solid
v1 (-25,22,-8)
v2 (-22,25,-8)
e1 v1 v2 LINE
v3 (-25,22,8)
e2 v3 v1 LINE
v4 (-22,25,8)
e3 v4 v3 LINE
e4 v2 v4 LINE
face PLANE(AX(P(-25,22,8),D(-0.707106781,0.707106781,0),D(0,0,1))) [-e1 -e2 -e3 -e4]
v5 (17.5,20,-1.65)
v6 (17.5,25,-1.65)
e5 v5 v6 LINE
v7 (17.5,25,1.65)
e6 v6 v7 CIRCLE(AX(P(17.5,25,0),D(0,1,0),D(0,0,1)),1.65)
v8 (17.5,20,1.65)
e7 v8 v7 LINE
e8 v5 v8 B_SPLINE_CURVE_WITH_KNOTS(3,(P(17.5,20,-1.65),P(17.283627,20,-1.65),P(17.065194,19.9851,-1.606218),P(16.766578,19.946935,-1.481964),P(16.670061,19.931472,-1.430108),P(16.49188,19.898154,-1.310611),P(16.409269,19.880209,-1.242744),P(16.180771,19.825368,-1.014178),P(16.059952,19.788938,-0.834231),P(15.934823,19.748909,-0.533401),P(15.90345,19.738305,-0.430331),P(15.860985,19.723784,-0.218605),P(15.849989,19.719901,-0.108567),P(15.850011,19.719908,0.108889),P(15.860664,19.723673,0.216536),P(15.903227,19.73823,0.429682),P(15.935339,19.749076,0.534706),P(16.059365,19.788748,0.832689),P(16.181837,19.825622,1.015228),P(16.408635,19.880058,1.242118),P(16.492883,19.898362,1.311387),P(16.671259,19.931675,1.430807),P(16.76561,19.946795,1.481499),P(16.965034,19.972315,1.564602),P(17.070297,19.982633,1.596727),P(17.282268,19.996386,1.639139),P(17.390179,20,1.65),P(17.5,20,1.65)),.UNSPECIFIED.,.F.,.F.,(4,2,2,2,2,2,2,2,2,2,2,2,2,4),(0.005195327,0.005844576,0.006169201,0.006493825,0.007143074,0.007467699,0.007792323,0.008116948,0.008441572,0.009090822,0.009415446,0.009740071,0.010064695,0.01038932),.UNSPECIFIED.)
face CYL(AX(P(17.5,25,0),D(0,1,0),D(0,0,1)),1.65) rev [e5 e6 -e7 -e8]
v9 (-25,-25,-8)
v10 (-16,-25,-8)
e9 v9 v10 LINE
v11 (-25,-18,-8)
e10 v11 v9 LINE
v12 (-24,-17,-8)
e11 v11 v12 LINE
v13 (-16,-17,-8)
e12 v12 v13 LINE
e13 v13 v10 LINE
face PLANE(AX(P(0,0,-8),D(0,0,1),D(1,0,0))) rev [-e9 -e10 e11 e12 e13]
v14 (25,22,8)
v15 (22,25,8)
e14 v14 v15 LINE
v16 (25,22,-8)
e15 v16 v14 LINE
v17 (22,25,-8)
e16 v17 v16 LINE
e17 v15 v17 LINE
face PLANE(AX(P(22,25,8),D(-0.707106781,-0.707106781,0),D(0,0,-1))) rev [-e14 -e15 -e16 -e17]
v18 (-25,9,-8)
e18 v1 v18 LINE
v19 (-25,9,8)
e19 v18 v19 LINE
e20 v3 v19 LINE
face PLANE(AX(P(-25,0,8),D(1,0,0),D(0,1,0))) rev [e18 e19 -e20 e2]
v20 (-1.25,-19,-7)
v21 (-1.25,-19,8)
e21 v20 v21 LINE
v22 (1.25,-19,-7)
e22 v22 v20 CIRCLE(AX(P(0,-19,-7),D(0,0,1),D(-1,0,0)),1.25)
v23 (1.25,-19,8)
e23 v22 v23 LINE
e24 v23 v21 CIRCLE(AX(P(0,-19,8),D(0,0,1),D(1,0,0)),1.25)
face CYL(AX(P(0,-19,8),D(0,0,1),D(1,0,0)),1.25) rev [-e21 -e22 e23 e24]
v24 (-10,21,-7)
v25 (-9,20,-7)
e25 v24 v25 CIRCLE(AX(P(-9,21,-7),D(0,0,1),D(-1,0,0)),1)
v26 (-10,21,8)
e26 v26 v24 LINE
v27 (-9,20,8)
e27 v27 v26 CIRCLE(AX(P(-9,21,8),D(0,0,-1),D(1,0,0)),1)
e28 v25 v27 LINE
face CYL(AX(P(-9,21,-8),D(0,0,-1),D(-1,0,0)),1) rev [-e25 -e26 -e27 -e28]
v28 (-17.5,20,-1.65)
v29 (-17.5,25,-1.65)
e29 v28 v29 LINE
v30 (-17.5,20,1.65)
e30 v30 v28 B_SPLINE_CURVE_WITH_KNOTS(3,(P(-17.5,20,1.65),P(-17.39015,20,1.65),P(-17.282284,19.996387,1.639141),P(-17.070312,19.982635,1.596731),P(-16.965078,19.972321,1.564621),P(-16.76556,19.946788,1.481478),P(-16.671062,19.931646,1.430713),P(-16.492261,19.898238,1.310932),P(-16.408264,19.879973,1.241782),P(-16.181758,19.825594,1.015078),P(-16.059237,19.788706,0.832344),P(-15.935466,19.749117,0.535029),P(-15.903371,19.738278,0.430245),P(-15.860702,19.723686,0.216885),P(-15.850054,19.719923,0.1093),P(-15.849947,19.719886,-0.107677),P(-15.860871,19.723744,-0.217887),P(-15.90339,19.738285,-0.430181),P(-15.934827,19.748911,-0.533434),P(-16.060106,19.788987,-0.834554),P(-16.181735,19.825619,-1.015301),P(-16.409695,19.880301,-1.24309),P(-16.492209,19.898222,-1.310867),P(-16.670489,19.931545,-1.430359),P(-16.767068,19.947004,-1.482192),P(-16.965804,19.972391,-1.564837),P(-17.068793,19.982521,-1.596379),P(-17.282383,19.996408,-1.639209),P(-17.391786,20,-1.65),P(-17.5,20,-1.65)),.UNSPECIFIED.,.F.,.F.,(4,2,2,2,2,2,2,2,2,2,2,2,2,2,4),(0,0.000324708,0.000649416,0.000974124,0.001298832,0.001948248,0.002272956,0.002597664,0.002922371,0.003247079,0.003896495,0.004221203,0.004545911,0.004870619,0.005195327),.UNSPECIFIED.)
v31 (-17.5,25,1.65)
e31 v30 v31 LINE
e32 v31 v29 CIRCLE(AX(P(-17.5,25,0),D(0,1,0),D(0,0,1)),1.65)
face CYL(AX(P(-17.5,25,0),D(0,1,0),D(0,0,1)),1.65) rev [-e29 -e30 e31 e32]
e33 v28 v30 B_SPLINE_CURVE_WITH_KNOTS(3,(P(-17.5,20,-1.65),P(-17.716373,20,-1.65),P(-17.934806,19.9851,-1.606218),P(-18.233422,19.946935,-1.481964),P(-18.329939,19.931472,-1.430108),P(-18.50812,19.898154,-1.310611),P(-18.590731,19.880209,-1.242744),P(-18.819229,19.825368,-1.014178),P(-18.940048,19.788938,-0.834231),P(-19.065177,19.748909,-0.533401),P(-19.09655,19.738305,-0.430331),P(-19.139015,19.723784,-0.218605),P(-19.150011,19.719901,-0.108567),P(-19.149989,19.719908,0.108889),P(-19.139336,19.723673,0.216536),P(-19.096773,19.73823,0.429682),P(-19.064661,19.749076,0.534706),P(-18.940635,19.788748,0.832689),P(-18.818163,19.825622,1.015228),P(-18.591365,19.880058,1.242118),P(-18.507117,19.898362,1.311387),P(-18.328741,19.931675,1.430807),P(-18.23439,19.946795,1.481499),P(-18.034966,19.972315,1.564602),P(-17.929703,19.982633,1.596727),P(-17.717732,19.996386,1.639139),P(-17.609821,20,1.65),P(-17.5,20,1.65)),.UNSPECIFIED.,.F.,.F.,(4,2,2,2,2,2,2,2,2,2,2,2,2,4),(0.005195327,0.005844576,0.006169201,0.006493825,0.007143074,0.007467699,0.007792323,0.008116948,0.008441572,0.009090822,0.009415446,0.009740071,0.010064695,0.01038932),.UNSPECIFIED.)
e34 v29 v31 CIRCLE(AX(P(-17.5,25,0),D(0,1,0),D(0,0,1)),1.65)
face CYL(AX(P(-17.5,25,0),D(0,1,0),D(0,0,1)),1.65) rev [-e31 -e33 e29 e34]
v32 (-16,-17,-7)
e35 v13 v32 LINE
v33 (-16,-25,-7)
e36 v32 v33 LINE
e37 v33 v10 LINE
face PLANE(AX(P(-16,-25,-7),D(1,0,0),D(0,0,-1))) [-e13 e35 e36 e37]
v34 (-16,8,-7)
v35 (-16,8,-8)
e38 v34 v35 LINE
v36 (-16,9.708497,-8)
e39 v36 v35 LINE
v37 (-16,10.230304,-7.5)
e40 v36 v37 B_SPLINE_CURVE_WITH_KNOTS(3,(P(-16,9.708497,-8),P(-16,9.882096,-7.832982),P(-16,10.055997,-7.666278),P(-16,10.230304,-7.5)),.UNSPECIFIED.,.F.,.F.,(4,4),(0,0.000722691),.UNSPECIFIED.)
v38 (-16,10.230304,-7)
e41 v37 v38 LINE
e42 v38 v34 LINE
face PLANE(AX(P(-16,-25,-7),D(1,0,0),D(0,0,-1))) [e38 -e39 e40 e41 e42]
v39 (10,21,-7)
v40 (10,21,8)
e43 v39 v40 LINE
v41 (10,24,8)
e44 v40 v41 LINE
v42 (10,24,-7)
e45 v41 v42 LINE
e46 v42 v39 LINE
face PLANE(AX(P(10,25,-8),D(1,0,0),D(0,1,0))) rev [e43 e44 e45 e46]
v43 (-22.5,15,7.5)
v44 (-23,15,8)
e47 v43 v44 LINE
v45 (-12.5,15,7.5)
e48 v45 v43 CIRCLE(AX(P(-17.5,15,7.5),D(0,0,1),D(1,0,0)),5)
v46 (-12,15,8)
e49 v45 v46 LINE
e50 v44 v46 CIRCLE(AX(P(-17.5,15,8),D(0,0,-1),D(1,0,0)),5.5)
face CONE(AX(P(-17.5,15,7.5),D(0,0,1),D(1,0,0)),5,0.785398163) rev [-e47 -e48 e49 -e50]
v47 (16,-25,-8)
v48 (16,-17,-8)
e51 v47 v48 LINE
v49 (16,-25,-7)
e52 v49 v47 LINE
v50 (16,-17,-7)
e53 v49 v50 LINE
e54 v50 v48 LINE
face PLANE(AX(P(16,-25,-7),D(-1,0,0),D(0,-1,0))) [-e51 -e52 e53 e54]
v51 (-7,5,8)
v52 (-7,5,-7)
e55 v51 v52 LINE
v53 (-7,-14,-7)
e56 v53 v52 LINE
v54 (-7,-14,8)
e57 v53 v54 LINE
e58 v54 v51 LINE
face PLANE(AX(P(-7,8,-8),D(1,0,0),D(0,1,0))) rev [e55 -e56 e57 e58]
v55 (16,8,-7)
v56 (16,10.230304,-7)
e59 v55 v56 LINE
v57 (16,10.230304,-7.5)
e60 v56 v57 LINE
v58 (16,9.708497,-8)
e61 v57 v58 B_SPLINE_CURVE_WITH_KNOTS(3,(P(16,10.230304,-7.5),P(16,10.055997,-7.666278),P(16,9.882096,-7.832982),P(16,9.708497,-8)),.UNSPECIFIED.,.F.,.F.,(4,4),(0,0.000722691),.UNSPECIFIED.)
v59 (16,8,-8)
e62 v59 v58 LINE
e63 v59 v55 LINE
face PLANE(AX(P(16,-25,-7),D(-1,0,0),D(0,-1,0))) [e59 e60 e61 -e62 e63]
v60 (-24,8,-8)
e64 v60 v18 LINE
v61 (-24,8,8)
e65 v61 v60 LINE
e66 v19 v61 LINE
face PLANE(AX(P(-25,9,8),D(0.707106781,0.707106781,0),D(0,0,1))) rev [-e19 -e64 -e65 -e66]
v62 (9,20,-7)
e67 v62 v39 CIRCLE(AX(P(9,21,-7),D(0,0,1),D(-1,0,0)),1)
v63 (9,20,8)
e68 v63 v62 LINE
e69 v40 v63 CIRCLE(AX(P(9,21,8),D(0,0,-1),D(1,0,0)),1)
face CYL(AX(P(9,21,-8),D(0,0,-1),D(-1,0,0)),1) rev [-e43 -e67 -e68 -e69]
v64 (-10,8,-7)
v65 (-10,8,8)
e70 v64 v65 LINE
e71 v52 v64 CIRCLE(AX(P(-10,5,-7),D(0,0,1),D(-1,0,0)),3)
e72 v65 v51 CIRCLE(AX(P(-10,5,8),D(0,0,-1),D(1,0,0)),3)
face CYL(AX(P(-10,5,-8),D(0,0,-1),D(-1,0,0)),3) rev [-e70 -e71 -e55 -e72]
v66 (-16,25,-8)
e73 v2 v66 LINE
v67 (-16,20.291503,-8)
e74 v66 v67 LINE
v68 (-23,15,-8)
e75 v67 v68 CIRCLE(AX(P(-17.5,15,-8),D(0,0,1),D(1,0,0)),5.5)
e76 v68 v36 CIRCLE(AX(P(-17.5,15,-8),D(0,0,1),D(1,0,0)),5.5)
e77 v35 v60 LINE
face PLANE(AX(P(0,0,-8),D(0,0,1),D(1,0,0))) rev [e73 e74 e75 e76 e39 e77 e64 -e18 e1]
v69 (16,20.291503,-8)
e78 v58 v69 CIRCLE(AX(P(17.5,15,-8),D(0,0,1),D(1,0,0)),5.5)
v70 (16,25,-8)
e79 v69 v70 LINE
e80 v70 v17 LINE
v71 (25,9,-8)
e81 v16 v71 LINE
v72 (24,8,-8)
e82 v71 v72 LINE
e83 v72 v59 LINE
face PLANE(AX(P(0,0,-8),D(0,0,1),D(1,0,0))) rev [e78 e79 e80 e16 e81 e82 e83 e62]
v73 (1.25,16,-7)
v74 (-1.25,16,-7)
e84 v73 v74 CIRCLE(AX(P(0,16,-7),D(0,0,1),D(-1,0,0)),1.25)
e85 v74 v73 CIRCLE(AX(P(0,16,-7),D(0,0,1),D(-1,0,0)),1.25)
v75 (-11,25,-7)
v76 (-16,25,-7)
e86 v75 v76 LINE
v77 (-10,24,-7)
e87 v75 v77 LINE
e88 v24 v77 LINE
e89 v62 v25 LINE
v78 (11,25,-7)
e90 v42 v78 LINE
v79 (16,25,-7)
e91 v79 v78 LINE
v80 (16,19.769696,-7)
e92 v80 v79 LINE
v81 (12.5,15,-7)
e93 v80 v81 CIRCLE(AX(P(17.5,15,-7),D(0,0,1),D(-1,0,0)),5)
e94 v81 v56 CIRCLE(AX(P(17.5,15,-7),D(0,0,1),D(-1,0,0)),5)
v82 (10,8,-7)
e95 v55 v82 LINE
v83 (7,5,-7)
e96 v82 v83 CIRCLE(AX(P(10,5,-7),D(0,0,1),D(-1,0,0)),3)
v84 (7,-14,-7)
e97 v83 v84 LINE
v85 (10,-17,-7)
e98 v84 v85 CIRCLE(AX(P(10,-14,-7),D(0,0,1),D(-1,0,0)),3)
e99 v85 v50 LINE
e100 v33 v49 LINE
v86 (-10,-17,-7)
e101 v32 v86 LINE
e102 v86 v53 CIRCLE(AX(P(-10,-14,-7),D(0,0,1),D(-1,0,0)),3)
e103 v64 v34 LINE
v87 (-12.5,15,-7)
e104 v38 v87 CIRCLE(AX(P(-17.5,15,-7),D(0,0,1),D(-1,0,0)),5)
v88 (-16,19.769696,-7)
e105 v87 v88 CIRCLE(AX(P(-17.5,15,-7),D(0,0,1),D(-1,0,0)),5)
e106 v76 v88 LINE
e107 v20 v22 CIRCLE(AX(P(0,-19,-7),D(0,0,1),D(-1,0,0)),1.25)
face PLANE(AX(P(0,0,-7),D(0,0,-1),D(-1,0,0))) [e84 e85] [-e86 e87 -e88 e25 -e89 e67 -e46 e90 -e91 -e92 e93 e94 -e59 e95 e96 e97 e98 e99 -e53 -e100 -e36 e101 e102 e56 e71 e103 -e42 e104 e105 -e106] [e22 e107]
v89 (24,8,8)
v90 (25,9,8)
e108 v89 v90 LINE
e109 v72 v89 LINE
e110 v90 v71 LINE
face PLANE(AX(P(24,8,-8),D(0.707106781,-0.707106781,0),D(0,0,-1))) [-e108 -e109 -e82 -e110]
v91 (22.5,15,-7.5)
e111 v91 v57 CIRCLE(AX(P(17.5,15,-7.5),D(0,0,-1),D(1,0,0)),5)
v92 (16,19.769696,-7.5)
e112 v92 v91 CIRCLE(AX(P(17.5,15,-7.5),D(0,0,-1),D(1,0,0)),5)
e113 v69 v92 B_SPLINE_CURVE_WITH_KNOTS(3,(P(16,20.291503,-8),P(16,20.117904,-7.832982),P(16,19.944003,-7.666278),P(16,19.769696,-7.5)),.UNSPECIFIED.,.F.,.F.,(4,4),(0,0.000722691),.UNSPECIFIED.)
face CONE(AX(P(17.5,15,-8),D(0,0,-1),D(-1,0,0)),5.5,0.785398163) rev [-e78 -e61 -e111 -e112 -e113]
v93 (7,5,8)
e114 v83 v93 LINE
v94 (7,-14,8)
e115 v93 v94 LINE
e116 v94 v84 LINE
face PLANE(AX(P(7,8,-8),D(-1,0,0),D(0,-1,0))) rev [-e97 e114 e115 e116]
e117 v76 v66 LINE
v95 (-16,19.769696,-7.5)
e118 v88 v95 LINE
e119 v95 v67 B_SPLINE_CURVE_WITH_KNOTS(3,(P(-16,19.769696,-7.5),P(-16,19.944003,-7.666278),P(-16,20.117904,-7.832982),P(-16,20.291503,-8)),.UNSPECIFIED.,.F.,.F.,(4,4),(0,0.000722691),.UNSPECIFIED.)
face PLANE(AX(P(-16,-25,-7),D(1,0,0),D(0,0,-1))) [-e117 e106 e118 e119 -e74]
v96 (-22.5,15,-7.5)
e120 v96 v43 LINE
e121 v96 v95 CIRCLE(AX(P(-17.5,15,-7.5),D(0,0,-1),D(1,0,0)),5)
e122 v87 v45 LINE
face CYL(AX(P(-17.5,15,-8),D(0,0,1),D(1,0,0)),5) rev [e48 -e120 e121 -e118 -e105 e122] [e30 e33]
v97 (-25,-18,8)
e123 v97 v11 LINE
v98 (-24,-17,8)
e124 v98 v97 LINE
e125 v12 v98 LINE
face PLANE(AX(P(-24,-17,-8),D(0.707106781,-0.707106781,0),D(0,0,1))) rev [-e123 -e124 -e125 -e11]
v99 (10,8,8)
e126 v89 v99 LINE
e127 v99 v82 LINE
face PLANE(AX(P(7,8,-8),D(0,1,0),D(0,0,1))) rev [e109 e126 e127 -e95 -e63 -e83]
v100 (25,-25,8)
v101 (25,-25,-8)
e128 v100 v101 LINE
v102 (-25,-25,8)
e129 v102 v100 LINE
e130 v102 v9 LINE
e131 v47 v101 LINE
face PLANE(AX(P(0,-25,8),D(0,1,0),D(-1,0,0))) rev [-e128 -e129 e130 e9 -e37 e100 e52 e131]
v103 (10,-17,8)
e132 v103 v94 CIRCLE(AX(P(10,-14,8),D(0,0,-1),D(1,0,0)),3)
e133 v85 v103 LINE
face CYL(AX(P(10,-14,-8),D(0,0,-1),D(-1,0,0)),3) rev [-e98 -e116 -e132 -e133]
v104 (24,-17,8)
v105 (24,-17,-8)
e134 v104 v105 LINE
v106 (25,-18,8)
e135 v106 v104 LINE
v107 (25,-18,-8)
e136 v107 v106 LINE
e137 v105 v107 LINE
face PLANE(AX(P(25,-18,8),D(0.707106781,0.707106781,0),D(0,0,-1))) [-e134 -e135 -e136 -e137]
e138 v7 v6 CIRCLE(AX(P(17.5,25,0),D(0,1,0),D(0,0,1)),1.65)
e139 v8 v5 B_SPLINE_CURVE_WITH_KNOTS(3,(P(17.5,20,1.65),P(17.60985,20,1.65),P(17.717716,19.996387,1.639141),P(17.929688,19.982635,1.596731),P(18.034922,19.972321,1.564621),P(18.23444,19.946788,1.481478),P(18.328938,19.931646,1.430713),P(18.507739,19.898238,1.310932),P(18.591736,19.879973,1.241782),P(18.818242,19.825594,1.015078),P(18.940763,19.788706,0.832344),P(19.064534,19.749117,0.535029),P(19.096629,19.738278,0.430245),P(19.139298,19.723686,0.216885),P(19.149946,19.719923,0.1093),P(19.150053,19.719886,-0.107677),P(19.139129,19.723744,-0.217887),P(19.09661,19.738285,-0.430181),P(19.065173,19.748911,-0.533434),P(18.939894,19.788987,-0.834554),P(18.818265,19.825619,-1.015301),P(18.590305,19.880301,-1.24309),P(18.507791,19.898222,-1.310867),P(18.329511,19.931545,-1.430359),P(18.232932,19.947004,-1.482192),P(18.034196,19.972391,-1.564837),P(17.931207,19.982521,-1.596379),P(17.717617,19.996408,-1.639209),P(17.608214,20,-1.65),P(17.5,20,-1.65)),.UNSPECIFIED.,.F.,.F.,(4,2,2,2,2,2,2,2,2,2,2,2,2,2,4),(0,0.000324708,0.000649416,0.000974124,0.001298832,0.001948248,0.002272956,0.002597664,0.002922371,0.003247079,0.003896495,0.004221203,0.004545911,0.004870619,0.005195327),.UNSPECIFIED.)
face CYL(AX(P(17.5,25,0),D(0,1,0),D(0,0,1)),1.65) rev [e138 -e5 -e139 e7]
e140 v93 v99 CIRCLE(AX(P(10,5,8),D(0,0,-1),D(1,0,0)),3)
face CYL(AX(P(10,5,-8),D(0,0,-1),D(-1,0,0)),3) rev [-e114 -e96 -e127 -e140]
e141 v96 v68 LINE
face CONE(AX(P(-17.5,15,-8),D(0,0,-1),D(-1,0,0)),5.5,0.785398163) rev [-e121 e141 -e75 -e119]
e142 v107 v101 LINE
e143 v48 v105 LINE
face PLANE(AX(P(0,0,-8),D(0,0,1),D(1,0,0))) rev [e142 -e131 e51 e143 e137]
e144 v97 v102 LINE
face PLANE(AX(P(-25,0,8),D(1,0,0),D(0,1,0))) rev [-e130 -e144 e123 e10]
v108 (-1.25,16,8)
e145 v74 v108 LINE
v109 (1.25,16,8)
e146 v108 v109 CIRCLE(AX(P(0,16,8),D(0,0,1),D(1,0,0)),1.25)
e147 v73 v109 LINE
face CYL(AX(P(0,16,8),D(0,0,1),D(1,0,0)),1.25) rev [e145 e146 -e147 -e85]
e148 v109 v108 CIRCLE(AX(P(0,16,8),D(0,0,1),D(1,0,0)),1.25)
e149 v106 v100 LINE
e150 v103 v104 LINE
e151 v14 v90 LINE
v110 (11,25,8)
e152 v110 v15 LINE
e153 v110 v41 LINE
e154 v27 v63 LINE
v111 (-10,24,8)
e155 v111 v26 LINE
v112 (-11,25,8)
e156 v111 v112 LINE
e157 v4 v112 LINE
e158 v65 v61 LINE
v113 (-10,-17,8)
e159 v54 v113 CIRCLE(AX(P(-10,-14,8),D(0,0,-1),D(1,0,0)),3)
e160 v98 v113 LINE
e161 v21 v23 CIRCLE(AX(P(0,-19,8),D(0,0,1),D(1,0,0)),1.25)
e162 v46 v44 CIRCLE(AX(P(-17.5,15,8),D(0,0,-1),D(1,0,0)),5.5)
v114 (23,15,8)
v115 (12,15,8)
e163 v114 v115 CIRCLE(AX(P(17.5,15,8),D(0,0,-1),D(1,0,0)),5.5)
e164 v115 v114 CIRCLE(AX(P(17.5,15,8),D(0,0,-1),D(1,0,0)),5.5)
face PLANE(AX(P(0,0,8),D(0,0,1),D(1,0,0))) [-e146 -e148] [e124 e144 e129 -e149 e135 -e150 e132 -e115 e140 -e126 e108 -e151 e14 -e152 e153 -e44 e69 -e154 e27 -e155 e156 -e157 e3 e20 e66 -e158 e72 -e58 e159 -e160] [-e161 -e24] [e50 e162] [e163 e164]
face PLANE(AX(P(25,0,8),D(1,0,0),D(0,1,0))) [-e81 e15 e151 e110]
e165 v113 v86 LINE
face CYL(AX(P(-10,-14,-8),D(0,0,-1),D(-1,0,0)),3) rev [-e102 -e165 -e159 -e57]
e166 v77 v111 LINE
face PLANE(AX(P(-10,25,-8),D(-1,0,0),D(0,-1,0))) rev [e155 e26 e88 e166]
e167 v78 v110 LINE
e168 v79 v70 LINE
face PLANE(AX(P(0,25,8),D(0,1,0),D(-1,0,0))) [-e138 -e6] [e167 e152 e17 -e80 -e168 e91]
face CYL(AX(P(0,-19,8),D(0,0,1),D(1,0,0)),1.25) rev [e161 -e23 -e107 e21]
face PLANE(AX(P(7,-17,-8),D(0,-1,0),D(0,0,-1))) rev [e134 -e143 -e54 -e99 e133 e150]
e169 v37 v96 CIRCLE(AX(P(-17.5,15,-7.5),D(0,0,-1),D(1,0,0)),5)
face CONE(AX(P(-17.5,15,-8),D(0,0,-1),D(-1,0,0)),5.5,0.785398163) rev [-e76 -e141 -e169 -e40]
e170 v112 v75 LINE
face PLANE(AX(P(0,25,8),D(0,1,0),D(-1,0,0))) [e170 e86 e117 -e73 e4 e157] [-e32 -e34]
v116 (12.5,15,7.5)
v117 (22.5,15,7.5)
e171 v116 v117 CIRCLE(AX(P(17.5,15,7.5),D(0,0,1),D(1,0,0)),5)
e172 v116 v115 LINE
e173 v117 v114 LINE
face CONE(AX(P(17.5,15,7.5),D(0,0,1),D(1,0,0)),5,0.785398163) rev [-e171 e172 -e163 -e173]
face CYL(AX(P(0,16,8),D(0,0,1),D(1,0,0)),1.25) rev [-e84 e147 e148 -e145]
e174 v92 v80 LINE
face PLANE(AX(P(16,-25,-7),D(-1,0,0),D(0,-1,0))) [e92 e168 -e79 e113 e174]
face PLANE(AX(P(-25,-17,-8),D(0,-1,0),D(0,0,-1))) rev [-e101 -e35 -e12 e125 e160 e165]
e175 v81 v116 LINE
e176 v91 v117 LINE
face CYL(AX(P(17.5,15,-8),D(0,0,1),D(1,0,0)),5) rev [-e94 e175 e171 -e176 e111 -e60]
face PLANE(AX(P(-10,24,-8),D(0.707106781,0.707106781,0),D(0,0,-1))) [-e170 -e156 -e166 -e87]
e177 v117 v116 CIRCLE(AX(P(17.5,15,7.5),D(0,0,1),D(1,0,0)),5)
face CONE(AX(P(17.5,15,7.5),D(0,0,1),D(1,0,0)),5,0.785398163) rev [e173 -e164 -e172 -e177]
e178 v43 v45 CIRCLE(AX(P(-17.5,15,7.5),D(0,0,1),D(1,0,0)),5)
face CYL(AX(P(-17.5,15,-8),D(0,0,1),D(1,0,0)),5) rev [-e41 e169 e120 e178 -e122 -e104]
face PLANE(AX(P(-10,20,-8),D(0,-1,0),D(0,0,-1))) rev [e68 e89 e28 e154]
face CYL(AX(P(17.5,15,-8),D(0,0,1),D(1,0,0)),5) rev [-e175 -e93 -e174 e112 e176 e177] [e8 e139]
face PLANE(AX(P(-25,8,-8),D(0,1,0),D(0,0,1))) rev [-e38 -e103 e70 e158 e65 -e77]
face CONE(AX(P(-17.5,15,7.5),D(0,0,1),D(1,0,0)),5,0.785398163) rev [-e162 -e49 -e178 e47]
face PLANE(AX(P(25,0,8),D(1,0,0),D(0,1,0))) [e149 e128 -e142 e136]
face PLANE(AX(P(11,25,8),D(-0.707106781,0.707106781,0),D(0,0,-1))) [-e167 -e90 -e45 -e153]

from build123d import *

# Parameters (mm, degrees)
BOSS_EXTRUDE1_DEPTH    = 8
SKETCH6_R              = 5
SKETCH6_W              = 18
SKETCH6_H              = 25
CUT_EXTRUDE1_DEPTH     = 39.807215824
M4_TAPPED_HOLE1_REACH  = 58.471
M4_TAPPED_HOLE1_BORE_R = 1.65
M3_TAPPED_HOLE1_D      = 2.5
SKETCH13_W             = 32
SKETCH13_H             = 50
CUT_EXTRUDE2_DEPTH     = 1
SKETCH14_W             = 20
SKETCH14_H             = 5
CUT_EXTRUDE3_DEPTH     = 39.80721593
CHAMFER1_SIZE          = 3
FILLET1_R              = 3
CHAMFER3_SIZE          = 1
CHAMFER4_SIZE          = 0.5
FILLET2_R              = 1


with BuildPart() as part:
    # Sketch1 → Boss-Extrude1 (new, symmetric)
    with BuildSketch(Plane.XY):
        Polygon((-25, -10), (-25, -25), (25, -25), (25, -10), (25, 25), (-25, 25), align=None)
    extrude(amount=BOSS_EXTRUDE1_DEPTH, both=True)

    # Sketch6 → Cut-Extrude1 (cut, through all)
    with BuildSketch(Plane.XY.offset(8)):
        with Locations((-17.5, 15)):
            Circle(SKETCH6_R)
        with Locations((17.5, 15)):
            Circle(SKETCH6_R)
        with Locations((16, -4.5)):
            Rectangle(SKETCH6_W, SKETCH6_H)
        with Locations((-16, -4.5)):
            Rectangle(SKETCH6_W, SKETCH6_H)
    extrude(amount=-CUT_EXTRUDE1_DEPTH, mode=Mode.SUBTRACT)

    # M4 Tapped Hole1 bore → M4 Tapped Hole1 (cut, up to next)
    with BuildSketch(Plane(origin=(0, 25, 0), x_dir=(1, 0, 0), z_dir=(0, 1, 0)), mode=Mode.PRIVATE) as m4_tapped_hole1_sk1:
        with Locations((-17.5, 0)):
            Circle(M4_TAPPED_HOLE1_BORE_R)
    m4_tapped_hole1_tool1 = extrude(m4_tapped_hole1_sk1.sketch, amount=-M4_TAPPED_HOLE1_REACH, mode=Mode.PRIVATE) & part.part
    # M4 Tapped Hole1 bore → M4 Tapped Hole1 (cut, up to next)
    with BuildSketch(Plane(origin=(0, 25, 0), x_dir=(1, 0, 0), z_dir=(0, 1, 0)), mode=Mode.PRIVATE) as m4_tapped_hole1_sk2:
        with Locations((17.5, 0)):
            Circle(M4_TAPPED_HOLE1_BORE_R)
    m4_tapped_hole1_tool2 = extrude(m4_tapped_hole1_sk2.sketch, amount=-M4_TAPPED_HOLE1_REACH, mode=Mode.PRIVATE) & part.part
    add(m4_tapped_hole1_tool1.solids().sort_by_distance((-17.5, 25, 0))[0], mode=Mode.SUBTRACT)
    add(m4_tapped_hole1_tool2.solids().sort_by_distance((17.5, 25, 0))[0], mode=Mode.SUBTRACT)

    # M3 Tapped Hole1 (through all)
    with Locations(Plane.XY.offset(8)):
        with Locations((0, -19), (0, 16)):
            Hole(M3_TAPPED_HOLE1_D / 2)

    # Sketch13 → Cut-Extrude2 (cut)
    with BuildSketch(Plane.XY.offset(-8)):
        Rectangle(SKETCH13_W, SKETCH13_H)
    extrude(amount=CUT_EXTRUDE2_DEPTH, mode=Mode.SUBTRACT)

    # Sketch14 → Cut-Extrude3 (cut, through all)
    with BuildSketch(Plane.XY.offset(8)):
        with Locations((0, 22.5)):
            Rectangle(SKETCH14_W, SKETCH14_H)
    extrude(amount=-CUT_EXTRUDE3_DEPTH, mode=Mode.SUBTRACT)

    # Chamfer1
    chamfer1_edges = [part.edges().sort_by_distance(p)[0] for p in [
        (-25, 25, 0),
        (25, 25, 0),
    ]]
    chamfer(chamfer1_edges, length=CHAMFER1_SIZE)

    # Fillet1
    fillet1_edges = [part.edges().sort_by_distance(p)[0] for p in [
        (-7, -17, 0.5),
        (-7, 8, 0.5),
        (7, -17, 0.5),
        (7, 8, 0.5),
    ]]
    fillet(fillet1_edges, radius=FILLET1_R)

    # Chamfer3
    chamfer3_edges = [part.edges().sort_by_distance(p)[0] for p in [
        (-10, 25, 0.5),
        (10, 25, 0.5),
        (25, 8, 0),
        (25, -17, 0),
        (-25, -17, 0),
        (-25, 8, 0),
    ]]
    chamfer(chamfer3_edges, length=CHAMFER3_SIZE)

    # Chamfer4
    chamfer4_edges = [part.edges().sort_by_distance(p)[0] for p in [
        (-22.5, 15, -8),
        (-22.5, 15, 8),
        (12.5, 15, 8),
        (20.458039892, 19.031128874, -8),
    ]]
    chamfer(chamfer4_edges, length=CHAMFER4_SIZE)

    # Fillet2
    fillet2_edges = [part.edges().sort_by_distance(p)[0] for p in [
        (-10, 20, 0.5),
        (10, 20, 0.5),
    ]]
    fillet(fillet2_edges, radius=FILLET2_R)


solid = part.part
